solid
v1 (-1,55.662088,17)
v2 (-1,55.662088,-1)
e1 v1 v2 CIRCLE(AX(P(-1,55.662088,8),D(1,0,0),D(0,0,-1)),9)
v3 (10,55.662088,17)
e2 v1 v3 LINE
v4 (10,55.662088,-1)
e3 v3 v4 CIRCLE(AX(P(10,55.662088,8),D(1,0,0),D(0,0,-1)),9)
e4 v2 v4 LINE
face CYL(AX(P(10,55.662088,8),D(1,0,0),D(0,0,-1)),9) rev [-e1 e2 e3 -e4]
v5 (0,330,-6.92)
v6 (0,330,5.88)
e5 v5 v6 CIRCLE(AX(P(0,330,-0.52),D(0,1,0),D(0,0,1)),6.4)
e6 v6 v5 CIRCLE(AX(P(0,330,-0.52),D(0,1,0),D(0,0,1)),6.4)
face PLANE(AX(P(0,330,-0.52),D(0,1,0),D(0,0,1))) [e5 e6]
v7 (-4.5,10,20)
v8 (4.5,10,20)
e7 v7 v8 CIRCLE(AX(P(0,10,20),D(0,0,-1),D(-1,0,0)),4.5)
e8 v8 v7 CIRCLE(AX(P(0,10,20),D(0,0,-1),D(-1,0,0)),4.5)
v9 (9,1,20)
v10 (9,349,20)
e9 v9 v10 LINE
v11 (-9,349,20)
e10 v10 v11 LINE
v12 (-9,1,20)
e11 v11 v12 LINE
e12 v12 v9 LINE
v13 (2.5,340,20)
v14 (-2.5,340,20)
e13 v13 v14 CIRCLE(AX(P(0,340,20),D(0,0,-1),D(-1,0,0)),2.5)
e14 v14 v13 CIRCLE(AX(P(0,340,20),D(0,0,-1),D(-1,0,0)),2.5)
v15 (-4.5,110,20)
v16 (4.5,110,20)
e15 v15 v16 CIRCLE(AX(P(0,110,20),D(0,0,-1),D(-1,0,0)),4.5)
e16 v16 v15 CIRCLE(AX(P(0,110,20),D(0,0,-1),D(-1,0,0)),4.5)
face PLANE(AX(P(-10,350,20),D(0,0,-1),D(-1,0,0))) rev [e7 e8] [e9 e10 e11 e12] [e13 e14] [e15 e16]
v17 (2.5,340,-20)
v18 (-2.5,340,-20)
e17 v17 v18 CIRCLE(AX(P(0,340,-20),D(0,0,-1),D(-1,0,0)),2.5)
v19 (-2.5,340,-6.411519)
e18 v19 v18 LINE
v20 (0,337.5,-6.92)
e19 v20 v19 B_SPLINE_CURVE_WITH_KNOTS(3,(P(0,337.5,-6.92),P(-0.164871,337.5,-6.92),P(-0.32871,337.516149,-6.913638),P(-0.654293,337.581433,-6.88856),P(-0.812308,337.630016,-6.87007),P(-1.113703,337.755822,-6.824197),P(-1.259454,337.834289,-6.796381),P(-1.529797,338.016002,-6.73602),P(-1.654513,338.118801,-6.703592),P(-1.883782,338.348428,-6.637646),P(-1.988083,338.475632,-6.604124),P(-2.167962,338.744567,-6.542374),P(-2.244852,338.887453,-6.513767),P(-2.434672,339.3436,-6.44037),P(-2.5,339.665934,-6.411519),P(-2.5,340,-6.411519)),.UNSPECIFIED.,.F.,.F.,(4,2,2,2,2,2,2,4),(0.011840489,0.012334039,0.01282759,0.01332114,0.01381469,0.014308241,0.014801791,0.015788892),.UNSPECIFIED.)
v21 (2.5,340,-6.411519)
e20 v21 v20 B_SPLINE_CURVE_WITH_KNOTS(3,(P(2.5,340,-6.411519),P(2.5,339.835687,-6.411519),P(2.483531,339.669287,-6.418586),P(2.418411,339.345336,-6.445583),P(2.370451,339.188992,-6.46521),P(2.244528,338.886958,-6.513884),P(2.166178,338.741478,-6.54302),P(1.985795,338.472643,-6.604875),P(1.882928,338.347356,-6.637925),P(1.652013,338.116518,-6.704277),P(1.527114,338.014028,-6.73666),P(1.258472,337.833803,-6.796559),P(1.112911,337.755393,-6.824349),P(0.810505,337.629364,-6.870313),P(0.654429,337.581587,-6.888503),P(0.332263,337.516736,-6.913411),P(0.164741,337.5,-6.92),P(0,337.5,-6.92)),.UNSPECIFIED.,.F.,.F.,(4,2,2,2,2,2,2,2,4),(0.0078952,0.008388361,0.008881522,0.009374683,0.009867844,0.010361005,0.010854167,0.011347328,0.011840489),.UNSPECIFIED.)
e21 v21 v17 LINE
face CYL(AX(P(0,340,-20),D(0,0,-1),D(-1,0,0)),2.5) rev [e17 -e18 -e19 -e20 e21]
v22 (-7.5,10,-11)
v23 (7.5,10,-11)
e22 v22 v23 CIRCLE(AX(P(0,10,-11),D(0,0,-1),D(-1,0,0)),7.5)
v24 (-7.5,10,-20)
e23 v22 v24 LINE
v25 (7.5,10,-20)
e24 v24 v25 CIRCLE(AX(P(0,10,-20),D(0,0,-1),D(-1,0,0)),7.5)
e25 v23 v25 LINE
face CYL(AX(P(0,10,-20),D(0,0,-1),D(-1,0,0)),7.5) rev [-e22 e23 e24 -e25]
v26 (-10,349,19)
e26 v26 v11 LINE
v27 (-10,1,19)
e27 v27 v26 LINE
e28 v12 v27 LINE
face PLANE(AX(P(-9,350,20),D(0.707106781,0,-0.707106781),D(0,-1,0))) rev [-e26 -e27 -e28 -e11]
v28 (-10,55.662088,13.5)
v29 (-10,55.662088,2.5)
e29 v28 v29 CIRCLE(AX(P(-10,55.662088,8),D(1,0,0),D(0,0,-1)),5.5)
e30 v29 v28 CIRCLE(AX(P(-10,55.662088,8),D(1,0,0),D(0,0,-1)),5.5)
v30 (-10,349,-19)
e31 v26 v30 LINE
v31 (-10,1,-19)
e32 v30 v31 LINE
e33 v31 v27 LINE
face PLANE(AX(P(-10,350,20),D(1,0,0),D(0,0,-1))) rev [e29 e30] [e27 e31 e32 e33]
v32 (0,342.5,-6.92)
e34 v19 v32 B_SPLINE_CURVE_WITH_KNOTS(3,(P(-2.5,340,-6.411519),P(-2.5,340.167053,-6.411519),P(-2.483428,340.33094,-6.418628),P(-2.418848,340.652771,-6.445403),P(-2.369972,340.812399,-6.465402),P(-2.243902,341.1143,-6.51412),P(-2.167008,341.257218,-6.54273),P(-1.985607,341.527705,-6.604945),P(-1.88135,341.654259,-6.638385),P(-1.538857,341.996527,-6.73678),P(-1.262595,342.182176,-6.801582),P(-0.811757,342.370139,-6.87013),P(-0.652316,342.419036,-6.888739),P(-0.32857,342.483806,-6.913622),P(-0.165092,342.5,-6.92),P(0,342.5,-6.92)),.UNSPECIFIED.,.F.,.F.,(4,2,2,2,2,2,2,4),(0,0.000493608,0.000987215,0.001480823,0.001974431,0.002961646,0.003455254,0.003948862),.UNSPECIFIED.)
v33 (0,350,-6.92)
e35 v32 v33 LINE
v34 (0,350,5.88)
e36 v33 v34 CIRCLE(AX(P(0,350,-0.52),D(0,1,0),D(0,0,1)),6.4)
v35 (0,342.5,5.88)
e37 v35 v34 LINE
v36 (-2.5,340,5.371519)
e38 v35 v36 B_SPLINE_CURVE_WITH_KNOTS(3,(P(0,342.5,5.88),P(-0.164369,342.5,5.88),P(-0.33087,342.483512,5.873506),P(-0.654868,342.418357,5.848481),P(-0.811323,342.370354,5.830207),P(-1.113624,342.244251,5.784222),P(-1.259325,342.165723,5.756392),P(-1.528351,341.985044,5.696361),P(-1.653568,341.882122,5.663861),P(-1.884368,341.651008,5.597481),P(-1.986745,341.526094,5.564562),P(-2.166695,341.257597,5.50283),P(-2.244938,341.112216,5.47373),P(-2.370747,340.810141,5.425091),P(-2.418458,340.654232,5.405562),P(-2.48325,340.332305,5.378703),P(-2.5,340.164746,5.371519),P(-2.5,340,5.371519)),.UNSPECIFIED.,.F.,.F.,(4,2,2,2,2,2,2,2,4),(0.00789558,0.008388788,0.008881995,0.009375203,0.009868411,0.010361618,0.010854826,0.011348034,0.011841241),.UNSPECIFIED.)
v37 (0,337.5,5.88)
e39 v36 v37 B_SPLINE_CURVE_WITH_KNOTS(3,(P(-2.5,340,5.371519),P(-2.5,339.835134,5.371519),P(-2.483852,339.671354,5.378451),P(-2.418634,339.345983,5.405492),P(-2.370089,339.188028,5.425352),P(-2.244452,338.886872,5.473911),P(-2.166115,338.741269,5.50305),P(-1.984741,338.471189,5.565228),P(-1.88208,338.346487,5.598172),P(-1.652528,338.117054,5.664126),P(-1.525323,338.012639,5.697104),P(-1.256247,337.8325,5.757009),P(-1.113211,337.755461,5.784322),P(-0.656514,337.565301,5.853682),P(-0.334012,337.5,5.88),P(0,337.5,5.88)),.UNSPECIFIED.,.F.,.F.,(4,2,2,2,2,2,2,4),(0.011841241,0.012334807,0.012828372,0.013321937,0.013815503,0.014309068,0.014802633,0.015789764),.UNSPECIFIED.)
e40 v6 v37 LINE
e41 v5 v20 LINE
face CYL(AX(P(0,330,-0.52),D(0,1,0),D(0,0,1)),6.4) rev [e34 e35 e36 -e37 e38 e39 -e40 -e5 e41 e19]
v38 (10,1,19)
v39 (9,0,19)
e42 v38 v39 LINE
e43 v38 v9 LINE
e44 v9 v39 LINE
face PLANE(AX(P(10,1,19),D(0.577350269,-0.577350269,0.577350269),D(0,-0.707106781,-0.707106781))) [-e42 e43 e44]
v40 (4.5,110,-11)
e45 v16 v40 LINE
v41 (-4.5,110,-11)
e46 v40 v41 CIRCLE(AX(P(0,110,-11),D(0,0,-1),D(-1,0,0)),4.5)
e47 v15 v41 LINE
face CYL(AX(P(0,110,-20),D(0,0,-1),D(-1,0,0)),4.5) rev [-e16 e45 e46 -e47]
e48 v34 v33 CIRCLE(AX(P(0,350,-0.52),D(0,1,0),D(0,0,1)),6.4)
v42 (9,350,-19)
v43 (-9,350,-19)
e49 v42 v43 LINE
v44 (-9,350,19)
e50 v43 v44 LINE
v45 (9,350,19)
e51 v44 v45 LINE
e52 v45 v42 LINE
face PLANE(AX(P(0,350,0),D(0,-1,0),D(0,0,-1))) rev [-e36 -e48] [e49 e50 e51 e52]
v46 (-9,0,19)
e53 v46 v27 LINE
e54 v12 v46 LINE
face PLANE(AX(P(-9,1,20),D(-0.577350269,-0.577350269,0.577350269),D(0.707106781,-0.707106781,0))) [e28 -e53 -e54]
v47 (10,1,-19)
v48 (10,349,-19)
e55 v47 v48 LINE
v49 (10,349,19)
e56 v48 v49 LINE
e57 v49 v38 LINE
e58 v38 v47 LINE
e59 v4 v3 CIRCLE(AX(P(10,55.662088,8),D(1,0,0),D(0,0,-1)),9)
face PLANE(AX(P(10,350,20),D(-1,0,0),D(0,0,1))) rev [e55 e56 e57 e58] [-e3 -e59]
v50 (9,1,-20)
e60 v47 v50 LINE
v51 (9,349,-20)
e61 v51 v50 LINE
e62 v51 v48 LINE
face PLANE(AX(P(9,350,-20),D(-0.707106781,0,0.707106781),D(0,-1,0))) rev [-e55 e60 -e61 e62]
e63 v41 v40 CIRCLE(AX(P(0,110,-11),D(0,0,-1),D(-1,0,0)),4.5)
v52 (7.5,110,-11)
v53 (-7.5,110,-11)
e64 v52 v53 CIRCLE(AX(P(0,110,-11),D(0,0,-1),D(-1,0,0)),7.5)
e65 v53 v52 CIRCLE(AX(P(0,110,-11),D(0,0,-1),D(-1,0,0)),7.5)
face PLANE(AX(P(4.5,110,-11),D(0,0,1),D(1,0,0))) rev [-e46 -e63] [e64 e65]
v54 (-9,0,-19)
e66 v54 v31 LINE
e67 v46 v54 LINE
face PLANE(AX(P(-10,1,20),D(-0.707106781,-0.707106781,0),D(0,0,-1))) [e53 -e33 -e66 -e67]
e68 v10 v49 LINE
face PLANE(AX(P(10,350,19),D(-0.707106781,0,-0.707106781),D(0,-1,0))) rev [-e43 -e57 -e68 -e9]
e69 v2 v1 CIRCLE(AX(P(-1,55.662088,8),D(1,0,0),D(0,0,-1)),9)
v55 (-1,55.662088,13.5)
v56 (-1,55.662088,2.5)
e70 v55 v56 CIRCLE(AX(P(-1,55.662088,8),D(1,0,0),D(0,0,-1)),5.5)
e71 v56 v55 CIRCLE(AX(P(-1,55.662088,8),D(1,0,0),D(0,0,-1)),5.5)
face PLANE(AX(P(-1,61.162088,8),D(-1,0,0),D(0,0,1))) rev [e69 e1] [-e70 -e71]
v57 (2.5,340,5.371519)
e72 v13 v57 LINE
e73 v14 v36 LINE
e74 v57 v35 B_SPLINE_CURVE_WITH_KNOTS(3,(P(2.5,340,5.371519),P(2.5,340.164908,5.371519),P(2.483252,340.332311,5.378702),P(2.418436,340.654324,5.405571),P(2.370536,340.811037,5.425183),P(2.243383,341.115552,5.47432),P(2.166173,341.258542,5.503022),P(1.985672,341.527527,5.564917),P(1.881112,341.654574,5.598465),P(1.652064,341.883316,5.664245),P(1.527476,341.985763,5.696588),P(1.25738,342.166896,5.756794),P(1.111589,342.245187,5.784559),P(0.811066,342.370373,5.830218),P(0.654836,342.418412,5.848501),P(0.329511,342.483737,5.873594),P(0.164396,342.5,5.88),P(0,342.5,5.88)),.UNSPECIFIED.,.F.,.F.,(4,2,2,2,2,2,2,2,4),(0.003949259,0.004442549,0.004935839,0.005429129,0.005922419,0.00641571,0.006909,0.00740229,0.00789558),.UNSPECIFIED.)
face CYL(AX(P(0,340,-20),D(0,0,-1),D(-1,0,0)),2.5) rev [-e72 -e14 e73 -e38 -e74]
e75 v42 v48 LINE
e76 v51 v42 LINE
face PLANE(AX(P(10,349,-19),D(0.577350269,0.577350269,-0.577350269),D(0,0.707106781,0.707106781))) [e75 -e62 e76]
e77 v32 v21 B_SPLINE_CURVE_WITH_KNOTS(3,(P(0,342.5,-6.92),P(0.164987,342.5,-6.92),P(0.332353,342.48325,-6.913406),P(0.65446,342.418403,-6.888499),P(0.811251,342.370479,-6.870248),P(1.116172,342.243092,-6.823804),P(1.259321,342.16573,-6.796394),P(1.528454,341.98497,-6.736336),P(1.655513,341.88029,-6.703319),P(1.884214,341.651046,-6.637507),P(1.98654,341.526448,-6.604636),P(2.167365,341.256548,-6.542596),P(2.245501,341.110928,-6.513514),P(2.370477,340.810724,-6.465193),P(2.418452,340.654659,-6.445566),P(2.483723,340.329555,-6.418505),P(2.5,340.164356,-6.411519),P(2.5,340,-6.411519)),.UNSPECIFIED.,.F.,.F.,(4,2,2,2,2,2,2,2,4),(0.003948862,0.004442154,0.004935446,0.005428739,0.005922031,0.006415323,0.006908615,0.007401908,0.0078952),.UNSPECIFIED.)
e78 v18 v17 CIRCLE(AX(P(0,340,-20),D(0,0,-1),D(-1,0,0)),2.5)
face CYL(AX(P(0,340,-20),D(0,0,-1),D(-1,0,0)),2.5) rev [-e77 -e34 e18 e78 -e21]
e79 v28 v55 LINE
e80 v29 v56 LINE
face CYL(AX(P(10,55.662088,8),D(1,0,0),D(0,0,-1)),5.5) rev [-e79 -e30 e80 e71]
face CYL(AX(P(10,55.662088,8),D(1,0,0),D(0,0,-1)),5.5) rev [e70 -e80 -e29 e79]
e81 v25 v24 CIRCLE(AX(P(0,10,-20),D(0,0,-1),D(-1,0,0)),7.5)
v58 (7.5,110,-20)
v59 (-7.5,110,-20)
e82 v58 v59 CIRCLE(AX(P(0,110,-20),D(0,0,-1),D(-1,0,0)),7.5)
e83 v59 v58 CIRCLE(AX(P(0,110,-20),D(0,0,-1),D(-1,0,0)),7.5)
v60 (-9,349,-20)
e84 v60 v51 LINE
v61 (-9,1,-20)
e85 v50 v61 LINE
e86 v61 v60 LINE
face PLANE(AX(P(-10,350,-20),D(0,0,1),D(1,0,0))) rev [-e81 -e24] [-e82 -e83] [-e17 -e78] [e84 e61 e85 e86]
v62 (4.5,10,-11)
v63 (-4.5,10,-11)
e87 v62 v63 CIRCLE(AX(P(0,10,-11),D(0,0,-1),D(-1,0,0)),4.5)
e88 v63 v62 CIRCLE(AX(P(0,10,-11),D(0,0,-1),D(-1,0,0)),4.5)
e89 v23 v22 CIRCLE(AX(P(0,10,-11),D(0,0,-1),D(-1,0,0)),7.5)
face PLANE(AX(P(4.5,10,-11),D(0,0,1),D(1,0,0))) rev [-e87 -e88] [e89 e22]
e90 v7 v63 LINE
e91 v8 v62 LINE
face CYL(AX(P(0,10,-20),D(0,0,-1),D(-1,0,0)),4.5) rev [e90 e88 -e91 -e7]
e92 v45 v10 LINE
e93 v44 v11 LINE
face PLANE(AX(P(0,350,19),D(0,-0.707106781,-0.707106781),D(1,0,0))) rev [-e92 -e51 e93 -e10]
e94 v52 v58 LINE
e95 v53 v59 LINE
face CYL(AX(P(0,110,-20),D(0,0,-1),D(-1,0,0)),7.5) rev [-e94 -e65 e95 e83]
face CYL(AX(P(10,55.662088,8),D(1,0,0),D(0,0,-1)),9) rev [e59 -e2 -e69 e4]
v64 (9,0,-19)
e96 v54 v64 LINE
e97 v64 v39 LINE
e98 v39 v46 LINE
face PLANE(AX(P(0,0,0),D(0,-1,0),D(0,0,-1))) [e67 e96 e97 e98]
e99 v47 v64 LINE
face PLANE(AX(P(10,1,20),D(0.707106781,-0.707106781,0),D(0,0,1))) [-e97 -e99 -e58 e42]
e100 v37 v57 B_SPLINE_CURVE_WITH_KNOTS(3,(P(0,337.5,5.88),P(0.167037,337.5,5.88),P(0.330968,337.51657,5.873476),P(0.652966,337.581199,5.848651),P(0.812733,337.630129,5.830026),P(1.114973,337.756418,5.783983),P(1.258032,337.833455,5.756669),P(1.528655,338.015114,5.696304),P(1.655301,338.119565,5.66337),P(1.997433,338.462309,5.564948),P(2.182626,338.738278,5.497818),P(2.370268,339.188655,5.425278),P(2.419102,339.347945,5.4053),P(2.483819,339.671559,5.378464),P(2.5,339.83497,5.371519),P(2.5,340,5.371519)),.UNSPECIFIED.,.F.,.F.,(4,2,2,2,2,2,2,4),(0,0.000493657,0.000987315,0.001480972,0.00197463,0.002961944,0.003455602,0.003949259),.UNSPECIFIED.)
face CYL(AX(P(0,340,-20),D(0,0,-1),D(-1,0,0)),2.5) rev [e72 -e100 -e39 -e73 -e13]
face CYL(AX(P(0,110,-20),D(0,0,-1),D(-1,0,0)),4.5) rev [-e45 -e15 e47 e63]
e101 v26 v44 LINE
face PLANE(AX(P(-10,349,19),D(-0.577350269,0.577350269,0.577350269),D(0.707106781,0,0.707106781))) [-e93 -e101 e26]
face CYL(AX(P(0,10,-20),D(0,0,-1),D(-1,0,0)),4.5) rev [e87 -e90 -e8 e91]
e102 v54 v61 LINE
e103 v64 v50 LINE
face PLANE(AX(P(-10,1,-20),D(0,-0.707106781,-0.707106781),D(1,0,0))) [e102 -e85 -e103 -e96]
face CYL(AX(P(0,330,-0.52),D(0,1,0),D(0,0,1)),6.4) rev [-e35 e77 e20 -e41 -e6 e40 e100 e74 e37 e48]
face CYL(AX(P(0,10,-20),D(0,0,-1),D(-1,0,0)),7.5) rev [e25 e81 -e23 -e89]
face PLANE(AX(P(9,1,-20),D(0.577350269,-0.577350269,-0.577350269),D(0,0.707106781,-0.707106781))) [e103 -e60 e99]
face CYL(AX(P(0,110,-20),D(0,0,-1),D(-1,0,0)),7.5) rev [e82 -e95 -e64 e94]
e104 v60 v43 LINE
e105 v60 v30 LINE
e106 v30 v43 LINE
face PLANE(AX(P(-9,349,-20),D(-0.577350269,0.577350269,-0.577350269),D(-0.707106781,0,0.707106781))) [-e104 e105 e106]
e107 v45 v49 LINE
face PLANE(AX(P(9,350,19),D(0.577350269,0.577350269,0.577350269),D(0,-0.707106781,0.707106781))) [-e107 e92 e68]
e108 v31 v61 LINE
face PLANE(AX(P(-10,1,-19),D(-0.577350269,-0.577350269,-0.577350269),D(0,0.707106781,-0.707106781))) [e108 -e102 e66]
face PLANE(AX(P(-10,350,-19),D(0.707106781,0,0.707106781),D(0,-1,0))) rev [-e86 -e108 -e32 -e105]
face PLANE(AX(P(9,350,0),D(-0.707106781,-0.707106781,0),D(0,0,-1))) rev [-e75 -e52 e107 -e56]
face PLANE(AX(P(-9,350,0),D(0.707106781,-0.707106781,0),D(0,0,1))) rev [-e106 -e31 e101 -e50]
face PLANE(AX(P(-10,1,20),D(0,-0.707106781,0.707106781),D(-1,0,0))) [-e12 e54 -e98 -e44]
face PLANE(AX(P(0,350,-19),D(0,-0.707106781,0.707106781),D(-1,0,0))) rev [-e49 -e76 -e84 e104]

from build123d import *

# Parameters (mm, degrees)
SKETCH_1_W                = 20
SKETCH_1_H                = 40
EXTRUDE_1_DEPTH           = 350
SKETCH_2_R                = 6.4
CUT_EXTRUDE_1_DEPTH       = 20
HOLE_WIZARD_M6_1_D        = 5
CHAMFER_1_SIZE            = 1
HOLE_WIZARD_1_D           = 9
HOLE_WIZARD_1_CBORE_D     = 15
HOLE_WIZARD_1_CBORE_DEPTH = 9
HOLE_WIZARD_2_D           = 11
HOLE_WIZARD_2_DEPTH       = 50
HOLE_WIZARD_2_CBORE_D     = 18
HOLE_WIZARD_2_CBORE_DEPTH = 11
HOLE_WIZARD_2_TIP         = 3.304733405


with BuildPart() as part:
    # 草图1 → 凸台-拉伸1 (new body)
    with BuildSketch(Plane(origin=(0, 0, 0), x_dir=(1, 0, 0), z_dir=(0, 1, 0))):
        Rectangle(SKETCH_1_W, SKETCH_1_H)
    extrude(amount=EXTRUDE_1_DEPTH)

    # 草图2 → 切除-拉伸1 (cut)
    with BuildSketch(Plane(origin=(0, 350, 0), x_dir=(1, 0, 0), z_dir=(0, 1, 0))):
        with Locations(Location((0, 0.52, 0), (0, 0, 270))):
            Circle(SKETCH_2_R)
    extrude(amount=-CUT_EXTRUDE_1_DEPTH, mode=Mode.SUBTRACT)

    # M6 螺纹孔1 (through all)
    with Locations(Plane(origin=(0, 0, -20), x_dir=(-1, 0, 0), z_dir=(0, 0, -1))):
        with Locations((0, 340)):
            Hole(HOLE_WIZARD_M6_1_D / 2)

    # 倒角1
    chamfer_1_edges = [part.edges().sort_by_distance(p)[0] for p in [
        (-10, 350, 0),
        (0, 350, 20),
        (10, 350, 0),
        (0, 0, 20),
        (-10, 0, 0),
        (0, 0, -20),
        (10, 0, 0),
        (0, 350, -20),
        (10, 175, 20),
        (-10, 175, 20),
        (-10, 175, -20),
        (10, 175, -20),
    ]]
    chamfer(chamfer_1_edges, length=CHAMFER_1_SIZE)

    # 打孔尺寸(%根据)内六角圆柱头螺钉的类型1 (through all)
    with Locations(Plane(origin=(0, 0, -20), x_dir=(-1, 0, 0), z_dir=(0, 0, -1))):
        with Locations((0, 10), (0, 110)):
            CounterBoreHole(HOLE_WIZARD_1_D / 2, HOLE_WIZARD_1_CBORE_D / 2, HOLE_WIZARD_1_CBORE_DEPTH)

    # 打孔尺寸(%根据)内六角圆柱头螺钉的类型2
    with Locations(Plane(origin=(10, 0, 0), x_dir=(0, 0, -1), z_dir=(1, 0, 0))):
        with Locations((-8, 55.662088154)):
            CounterBoreHole(HOLE_WIZARD_2_D / 2, HOLE_WIZARD_2_CBORE_D / 2, HOLE_WIZARD_2_CBORE_DEPTH, depth=HOLE_WIZARD_2_DEPTH)
            with Locations((0, 0, -(HOLE_WIZARD_2_DEPTH + HOLE_WIZARD_2_TIP / 2))):  # 118° drill point
                Cone(0, HOLE_WIZARD_2_D / 2, HOLE_WIZARD_2_TIP, mode=Mode.SUBTRACT)


solid = part.part
